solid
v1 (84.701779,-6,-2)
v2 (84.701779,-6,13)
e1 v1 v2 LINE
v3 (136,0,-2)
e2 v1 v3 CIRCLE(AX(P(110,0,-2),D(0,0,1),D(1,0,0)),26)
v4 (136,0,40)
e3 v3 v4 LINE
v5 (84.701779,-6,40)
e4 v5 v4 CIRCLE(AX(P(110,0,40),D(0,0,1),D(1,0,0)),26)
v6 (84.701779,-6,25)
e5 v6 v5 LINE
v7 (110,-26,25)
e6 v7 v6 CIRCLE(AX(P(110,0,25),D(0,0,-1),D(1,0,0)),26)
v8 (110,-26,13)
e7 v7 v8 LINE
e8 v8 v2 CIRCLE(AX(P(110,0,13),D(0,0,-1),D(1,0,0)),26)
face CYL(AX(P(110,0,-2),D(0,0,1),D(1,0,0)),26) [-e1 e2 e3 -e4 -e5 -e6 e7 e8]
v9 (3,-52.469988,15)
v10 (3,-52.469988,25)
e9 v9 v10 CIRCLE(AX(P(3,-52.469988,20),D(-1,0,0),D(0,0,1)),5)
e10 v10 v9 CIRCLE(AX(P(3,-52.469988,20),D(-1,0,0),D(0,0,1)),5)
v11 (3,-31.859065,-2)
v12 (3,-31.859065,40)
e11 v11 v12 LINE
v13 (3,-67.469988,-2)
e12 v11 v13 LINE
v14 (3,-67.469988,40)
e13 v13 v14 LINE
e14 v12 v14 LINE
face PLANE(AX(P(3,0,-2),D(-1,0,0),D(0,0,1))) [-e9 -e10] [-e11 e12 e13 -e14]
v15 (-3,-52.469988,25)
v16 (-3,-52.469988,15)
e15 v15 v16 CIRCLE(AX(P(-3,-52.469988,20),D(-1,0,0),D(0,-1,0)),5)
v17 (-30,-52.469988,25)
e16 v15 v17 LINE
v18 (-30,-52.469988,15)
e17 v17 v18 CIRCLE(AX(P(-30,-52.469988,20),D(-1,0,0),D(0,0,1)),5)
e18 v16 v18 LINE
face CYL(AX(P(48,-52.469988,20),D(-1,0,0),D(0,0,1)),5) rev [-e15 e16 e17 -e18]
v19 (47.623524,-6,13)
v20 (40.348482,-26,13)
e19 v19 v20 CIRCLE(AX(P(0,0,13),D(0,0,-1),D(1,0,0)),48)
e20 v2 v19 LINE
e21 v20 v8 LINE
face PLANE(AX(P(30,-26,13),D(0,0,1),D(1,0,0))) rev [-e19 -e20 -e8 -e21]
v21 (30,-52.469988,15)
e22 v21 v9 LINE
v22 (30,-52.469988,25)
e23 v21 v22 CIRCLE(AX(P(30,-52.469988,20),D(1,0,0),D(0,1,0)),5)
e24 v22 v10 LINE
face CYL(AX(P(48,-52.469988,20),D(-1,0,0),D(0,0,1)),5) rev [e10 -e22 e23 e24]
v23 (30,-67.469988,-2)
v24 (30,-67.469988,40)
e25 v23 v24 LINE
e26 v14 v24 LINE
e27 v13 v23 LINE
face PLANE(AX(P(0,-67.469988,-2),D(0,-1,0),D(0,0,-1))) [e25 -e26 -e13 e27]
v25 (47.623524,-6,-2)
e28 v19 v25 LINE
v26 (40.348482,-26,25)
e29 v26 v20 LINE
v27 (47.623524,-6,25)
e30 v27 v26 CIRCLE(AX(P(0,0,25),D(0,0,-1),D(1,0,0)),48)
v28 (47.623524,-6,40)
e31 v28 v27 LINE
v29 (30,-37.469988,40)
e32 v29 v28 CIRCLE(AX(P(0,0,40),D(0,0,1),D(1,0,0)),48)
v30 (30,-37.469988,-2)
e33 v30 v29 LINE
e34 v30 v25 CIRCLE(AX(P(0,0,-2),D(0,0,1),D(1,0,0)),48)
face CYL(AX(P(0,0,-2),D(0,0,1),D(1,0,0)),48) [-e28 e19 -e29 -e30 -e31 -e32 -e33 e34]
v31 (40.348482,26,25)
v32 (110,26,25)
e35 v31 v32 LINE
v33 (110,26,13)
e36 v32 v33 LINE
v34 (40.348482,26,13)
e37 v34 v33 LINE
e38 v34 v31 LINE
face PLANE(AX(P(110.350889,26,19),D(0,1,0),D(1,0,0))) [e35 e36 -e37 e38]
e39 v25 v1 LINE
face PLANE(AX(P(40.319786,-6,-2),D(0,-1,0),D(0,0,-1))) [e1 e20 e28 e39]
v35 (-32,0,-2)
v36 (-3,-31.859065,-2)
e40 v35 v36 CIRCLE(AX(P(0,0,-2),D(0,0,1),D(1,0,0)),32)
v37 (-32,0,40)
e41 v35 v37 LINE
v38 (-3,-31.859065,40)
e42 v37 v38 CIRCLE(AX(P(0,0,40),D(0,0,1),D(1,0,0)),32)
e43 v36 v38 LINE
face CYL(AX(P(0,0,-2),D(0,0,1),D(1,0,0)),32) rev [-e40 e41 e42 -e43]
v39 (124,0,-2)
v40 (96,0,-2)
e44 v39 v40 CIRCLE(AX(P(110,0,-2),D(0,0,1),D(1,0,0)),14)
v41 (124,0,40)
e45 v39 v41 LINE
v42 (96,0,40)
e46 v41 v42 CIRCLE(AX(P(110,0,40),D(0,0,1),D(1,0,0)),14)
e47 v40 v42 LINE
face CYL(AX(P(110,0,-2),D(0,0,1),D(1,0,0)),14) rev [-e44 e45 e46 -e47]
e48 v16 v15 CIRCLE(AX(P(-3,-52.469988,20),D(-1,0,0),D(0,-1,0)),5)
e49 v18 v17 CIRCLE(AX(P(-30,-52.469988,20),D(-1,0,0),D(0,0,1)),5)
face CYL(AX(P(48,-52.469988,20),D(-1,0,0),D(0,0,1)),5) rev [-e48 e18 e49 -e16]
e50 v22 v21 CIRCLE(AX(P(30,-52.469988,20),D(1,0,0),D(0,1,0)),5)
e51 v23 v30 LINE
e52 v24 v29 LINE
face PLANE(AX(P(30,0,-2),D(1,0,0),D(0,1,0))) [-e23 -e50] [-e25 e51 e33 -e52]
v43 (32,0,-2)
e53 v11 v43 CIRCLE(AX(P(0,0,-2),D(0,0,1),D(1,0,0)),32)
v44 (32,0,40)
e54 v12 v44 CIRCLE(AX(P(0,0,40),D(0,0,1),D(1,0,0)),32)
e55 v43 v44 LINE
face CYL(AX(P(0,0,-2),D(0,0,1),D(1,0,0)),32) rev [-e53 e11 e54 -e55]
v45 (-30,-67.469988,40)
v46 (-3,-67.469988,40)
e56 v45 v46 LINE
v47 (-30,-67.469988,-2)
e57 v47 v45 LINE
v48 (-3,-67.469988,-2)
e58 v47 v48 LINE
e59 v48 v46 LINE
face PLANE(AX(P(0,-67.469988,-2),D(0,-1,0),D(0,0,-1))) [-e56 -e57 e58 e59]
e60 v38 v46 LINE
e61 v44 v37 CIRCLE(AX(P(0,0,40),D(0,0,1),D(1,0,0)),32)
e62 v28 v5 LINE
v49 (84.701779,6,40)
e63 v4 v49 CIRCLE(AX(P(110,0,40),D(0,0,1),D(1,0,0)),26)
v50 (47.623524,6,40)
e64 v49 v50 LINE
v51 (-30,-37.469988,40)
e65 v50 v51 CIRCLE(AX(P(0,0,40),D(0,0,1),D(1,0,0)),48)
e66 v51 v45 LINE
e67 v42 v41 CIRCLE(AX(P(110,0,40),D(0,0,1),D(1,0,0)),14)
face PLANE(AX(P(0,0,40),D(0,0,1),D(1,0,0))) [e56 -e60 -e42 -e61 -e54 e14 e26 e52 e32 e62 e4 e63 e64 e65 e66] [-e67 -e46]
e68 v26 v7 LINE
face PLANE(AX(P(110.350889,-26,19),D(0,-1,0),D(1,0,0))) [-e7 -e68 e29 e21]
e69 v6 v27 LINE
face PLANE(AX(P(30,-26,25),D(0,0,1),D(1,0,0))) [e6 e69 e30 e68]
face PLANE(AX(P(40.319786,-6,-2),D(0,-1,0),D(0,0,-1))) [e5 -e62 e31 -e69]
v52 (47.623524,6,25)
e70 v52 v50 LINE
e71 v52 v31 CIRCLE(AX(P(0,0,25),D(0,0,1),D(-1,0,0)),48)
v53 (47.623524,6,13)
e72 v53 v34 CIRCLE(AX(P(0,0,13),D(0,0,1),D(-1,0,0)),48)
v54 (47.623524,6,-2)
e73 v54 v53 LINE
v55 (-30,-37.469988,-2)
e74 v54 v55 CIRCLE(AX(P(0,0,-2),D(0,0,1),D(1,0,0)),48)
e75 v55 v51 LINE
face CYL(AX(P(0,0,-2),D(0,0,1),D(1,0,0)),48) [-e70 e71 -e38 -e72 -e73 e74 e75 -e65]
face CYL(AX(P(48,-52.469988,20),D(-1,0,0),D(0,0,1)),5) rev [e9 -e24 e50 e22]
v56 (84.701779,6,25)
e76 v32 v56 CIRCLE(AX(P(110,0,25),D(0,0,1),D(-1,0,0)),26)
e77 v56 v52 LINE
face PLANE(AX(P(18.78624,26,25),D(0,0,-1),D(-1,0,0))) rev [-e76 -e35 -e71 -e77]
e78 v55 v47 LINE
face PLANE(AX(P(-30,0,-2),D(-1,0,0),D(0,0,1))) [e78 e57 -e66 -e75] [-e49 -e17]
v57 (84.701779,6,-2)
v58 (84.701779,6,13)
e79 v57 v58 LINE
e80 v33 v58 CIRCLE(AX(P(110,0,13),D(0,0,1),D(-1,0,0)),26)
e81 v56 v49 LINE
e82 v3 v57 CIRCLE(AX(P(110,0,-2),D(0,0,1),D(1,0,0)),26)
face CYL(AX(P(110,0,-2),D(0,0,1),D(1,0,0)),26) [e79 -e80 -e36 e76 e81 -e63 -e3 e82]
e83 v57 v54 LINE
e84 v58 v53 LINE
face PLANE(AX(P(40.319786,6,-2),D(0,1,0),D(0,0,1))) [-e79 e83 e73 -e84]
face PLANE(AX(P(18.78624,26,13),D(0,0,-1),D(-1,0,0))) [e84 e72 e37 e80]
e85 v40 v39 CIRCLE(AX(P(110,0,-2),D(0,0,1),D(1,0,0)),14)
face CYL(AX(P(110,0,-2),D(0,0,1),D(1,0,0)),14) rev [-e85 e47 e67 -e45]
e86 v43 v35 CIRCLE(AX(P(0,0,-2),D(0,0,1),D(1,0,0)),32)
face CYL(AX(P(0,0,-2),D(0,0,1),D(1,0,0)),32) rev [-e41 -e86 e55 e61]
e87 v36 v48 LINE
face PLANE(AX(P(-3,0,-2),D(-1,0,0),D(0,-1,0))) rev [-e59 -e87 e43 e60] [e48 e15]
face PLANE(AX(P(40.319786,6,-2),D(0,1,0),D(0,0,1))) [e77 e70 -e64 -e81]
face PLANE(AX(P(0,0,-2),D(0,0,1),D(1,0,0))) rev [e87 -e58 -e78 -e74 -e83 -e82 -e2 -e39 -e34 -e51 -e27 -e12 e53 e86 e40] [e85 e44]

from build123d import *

# Parameters (mm, degrees)
CLAMP_BODY_DEPTH          = 40
CLAMP_BODY_DEPTH_BACK     = 2
CLAMP_SCREW_HOLE_SKETCH_R = 5
CLAMP_SCREW_HOLE_10_DEPTH = 111.617355236
PIVOT_ARM_SKETCH_R        = 14
PIVOT_ARM_AND_BOSS_DEPTH  = 42
ARM_RIB_REACH             = 171.802
ARM_RIB_SKETCH_WALLS_W    = 433.168174749
ARM_RIB_SKETCH_WALLS_H    = 12
CLAMP_RIB_REACH           = 161.912
CLAMP_RIB_SKETCH_WALLS_W  = 402.175841481
CLAMP_RIB_SKETCH_WALLS_H  = 12
BORE_START                = -60
BORE_SKETCH_R             = 32
BORE_64_DEPTH             = 60


with BuildPart() as part:
    # Clamp Body Sketch → Clamp Body (new, two sides: drawn at the far end of the back side and taken through both)
    with BuildSketch(Plane.XY.offset(-CLAMP_BODY_DEPTH_BACK)):
        with BuildLine():
            ThreePointArc((30, -37.46998799), (17.305444592, -44.771883895), (3, -47.906158268))
            Line((3, -47.906158268), (3, -53.969677407))
            Line((3, -53.969677407), (3, -67.46998799))
            Line((3, -67.46998799), (30, -67.46998799))
            Line((30, -67.46998799), (30, -37.46998799))
        make_face()
        with BuildLine():
            ThreePointArc((3, -47.906158268), (0, 48), (-3, -47.906158268))
            Line((-3, -47.906158268), (-3, -31.859064644))
            ThreePointArc((-3, -31.859064644), (0, 32), (3, -31.859064644))
            Line((3, -31.859064644), (3, -47.906158268))
        make_face()
        with BuildLine():
            ThreePointArc((-3, -47.906158268), (-17.305444592, -44.771883895), (-30, -37.46998799))
            Line((-30, -37.46998799), (-30, -67.46998799))
            Line((-30, -67.46998799), (-3, -67.46998799))
            Line((-3, -67.46998799), (-3, -47.906158268))
        make_face()
    extrude(amount=CLAMP_BODY_DEPTH + CLAMP_BODY_DEPTH_BACK)

    # Clamp Screw Hole Sketch → Clamp Screw Hole _10 (cut, through all)
    with BuildSketch(Plane.ZY.offset(30)):
        with Locations((20, -52.46998799)):
            Circle(CLAMP_SCREW_HOLE_SKETCH_R)
    extrude(amount=-CLAMP_SCREW_HOLE_10_DEPTH, mode=Mode.SUBTRACT)

    # Pivot Arm Sketch → Pivot Arm and Boss (add)
    with BuildSketch(Plane.XY.offset(40)):
        with BuildLine():
            Line((40.319786094, 6), (40.319786094, -6))
            Line((40.319786094, -6), (84.701778719, -6))
            ThreePointArc((84.701778719, -6), (136, 0), (84.701778719, 6))
            Line((84.701778719, 6), (40.319786094, 6))
        make_face()
        with Locations((110, 0)):
            Circle(PIVOT_ARM_SKETCH_R, mode=Mode.SUBTRACT)
    extrude(amount=-PIVOT_ARM_AND_BOSS_DEPTH)

    # Arm Rib Sketch walls → Arm Rib (add, up to next)
    with BuildSketch(Plane(origin=(0, 26, 0), x_dir=(1, 0, 0), z_dir=(0, 1, 0)), mode=Mode.PRIVATE) as arm_rib_sk1:
        with Locations((64.5685648, -19)):
            Rectangle(ARM_RIB_SKETCH_WALLS_W, ARM_RIB_SKETCH_WALLS_H)
    arm_rib_tool1 = extrude(arm_rib_sk1.sketch, amount=-ARM_RIB_REACH, mode=Mode.PRIVATE) - part.part
    add(arm_rib_tool1.solids().sort_by_distance((64.568564799, 26, 19))[0])

    # Clamp Rib Sketch walls → Clamp Rib (add, up to next)
    with BuildSketch(Plane(origin=(0, -26, 0), x_dir=(1, 0, 0), z_dir=(0, 1, 0)), mode=Mode.PRIVATE) as clamp_rib_sk1:
        with Locations((70.17544468, -19)):
            Rectangle(CLAMP_RIB_SKETCH_WALLS_W, CLAMP_RIB_SKETCH_WALLS_H)
    clamp_rib_tool1 = extrude(clamp_rib_sk1.sketch, amount=CLAMP_RIB_REACH, mode=Mode.PRIVATE) - part.part
    add(clamp_rib_tool1.solids().sort_by_distance((70.17544468, -26, 19))[0])

    # Bore Sketch → Bore _64 (cut)
    with BuildSketch(Plane.XY.offset(40).offset(BORE_START)):
        Circle(BORE_SKETCH_R)
    extrude(amount=BORE_64_DEPTH, mode=Mode.SUBTRACT)


solid = part.part
